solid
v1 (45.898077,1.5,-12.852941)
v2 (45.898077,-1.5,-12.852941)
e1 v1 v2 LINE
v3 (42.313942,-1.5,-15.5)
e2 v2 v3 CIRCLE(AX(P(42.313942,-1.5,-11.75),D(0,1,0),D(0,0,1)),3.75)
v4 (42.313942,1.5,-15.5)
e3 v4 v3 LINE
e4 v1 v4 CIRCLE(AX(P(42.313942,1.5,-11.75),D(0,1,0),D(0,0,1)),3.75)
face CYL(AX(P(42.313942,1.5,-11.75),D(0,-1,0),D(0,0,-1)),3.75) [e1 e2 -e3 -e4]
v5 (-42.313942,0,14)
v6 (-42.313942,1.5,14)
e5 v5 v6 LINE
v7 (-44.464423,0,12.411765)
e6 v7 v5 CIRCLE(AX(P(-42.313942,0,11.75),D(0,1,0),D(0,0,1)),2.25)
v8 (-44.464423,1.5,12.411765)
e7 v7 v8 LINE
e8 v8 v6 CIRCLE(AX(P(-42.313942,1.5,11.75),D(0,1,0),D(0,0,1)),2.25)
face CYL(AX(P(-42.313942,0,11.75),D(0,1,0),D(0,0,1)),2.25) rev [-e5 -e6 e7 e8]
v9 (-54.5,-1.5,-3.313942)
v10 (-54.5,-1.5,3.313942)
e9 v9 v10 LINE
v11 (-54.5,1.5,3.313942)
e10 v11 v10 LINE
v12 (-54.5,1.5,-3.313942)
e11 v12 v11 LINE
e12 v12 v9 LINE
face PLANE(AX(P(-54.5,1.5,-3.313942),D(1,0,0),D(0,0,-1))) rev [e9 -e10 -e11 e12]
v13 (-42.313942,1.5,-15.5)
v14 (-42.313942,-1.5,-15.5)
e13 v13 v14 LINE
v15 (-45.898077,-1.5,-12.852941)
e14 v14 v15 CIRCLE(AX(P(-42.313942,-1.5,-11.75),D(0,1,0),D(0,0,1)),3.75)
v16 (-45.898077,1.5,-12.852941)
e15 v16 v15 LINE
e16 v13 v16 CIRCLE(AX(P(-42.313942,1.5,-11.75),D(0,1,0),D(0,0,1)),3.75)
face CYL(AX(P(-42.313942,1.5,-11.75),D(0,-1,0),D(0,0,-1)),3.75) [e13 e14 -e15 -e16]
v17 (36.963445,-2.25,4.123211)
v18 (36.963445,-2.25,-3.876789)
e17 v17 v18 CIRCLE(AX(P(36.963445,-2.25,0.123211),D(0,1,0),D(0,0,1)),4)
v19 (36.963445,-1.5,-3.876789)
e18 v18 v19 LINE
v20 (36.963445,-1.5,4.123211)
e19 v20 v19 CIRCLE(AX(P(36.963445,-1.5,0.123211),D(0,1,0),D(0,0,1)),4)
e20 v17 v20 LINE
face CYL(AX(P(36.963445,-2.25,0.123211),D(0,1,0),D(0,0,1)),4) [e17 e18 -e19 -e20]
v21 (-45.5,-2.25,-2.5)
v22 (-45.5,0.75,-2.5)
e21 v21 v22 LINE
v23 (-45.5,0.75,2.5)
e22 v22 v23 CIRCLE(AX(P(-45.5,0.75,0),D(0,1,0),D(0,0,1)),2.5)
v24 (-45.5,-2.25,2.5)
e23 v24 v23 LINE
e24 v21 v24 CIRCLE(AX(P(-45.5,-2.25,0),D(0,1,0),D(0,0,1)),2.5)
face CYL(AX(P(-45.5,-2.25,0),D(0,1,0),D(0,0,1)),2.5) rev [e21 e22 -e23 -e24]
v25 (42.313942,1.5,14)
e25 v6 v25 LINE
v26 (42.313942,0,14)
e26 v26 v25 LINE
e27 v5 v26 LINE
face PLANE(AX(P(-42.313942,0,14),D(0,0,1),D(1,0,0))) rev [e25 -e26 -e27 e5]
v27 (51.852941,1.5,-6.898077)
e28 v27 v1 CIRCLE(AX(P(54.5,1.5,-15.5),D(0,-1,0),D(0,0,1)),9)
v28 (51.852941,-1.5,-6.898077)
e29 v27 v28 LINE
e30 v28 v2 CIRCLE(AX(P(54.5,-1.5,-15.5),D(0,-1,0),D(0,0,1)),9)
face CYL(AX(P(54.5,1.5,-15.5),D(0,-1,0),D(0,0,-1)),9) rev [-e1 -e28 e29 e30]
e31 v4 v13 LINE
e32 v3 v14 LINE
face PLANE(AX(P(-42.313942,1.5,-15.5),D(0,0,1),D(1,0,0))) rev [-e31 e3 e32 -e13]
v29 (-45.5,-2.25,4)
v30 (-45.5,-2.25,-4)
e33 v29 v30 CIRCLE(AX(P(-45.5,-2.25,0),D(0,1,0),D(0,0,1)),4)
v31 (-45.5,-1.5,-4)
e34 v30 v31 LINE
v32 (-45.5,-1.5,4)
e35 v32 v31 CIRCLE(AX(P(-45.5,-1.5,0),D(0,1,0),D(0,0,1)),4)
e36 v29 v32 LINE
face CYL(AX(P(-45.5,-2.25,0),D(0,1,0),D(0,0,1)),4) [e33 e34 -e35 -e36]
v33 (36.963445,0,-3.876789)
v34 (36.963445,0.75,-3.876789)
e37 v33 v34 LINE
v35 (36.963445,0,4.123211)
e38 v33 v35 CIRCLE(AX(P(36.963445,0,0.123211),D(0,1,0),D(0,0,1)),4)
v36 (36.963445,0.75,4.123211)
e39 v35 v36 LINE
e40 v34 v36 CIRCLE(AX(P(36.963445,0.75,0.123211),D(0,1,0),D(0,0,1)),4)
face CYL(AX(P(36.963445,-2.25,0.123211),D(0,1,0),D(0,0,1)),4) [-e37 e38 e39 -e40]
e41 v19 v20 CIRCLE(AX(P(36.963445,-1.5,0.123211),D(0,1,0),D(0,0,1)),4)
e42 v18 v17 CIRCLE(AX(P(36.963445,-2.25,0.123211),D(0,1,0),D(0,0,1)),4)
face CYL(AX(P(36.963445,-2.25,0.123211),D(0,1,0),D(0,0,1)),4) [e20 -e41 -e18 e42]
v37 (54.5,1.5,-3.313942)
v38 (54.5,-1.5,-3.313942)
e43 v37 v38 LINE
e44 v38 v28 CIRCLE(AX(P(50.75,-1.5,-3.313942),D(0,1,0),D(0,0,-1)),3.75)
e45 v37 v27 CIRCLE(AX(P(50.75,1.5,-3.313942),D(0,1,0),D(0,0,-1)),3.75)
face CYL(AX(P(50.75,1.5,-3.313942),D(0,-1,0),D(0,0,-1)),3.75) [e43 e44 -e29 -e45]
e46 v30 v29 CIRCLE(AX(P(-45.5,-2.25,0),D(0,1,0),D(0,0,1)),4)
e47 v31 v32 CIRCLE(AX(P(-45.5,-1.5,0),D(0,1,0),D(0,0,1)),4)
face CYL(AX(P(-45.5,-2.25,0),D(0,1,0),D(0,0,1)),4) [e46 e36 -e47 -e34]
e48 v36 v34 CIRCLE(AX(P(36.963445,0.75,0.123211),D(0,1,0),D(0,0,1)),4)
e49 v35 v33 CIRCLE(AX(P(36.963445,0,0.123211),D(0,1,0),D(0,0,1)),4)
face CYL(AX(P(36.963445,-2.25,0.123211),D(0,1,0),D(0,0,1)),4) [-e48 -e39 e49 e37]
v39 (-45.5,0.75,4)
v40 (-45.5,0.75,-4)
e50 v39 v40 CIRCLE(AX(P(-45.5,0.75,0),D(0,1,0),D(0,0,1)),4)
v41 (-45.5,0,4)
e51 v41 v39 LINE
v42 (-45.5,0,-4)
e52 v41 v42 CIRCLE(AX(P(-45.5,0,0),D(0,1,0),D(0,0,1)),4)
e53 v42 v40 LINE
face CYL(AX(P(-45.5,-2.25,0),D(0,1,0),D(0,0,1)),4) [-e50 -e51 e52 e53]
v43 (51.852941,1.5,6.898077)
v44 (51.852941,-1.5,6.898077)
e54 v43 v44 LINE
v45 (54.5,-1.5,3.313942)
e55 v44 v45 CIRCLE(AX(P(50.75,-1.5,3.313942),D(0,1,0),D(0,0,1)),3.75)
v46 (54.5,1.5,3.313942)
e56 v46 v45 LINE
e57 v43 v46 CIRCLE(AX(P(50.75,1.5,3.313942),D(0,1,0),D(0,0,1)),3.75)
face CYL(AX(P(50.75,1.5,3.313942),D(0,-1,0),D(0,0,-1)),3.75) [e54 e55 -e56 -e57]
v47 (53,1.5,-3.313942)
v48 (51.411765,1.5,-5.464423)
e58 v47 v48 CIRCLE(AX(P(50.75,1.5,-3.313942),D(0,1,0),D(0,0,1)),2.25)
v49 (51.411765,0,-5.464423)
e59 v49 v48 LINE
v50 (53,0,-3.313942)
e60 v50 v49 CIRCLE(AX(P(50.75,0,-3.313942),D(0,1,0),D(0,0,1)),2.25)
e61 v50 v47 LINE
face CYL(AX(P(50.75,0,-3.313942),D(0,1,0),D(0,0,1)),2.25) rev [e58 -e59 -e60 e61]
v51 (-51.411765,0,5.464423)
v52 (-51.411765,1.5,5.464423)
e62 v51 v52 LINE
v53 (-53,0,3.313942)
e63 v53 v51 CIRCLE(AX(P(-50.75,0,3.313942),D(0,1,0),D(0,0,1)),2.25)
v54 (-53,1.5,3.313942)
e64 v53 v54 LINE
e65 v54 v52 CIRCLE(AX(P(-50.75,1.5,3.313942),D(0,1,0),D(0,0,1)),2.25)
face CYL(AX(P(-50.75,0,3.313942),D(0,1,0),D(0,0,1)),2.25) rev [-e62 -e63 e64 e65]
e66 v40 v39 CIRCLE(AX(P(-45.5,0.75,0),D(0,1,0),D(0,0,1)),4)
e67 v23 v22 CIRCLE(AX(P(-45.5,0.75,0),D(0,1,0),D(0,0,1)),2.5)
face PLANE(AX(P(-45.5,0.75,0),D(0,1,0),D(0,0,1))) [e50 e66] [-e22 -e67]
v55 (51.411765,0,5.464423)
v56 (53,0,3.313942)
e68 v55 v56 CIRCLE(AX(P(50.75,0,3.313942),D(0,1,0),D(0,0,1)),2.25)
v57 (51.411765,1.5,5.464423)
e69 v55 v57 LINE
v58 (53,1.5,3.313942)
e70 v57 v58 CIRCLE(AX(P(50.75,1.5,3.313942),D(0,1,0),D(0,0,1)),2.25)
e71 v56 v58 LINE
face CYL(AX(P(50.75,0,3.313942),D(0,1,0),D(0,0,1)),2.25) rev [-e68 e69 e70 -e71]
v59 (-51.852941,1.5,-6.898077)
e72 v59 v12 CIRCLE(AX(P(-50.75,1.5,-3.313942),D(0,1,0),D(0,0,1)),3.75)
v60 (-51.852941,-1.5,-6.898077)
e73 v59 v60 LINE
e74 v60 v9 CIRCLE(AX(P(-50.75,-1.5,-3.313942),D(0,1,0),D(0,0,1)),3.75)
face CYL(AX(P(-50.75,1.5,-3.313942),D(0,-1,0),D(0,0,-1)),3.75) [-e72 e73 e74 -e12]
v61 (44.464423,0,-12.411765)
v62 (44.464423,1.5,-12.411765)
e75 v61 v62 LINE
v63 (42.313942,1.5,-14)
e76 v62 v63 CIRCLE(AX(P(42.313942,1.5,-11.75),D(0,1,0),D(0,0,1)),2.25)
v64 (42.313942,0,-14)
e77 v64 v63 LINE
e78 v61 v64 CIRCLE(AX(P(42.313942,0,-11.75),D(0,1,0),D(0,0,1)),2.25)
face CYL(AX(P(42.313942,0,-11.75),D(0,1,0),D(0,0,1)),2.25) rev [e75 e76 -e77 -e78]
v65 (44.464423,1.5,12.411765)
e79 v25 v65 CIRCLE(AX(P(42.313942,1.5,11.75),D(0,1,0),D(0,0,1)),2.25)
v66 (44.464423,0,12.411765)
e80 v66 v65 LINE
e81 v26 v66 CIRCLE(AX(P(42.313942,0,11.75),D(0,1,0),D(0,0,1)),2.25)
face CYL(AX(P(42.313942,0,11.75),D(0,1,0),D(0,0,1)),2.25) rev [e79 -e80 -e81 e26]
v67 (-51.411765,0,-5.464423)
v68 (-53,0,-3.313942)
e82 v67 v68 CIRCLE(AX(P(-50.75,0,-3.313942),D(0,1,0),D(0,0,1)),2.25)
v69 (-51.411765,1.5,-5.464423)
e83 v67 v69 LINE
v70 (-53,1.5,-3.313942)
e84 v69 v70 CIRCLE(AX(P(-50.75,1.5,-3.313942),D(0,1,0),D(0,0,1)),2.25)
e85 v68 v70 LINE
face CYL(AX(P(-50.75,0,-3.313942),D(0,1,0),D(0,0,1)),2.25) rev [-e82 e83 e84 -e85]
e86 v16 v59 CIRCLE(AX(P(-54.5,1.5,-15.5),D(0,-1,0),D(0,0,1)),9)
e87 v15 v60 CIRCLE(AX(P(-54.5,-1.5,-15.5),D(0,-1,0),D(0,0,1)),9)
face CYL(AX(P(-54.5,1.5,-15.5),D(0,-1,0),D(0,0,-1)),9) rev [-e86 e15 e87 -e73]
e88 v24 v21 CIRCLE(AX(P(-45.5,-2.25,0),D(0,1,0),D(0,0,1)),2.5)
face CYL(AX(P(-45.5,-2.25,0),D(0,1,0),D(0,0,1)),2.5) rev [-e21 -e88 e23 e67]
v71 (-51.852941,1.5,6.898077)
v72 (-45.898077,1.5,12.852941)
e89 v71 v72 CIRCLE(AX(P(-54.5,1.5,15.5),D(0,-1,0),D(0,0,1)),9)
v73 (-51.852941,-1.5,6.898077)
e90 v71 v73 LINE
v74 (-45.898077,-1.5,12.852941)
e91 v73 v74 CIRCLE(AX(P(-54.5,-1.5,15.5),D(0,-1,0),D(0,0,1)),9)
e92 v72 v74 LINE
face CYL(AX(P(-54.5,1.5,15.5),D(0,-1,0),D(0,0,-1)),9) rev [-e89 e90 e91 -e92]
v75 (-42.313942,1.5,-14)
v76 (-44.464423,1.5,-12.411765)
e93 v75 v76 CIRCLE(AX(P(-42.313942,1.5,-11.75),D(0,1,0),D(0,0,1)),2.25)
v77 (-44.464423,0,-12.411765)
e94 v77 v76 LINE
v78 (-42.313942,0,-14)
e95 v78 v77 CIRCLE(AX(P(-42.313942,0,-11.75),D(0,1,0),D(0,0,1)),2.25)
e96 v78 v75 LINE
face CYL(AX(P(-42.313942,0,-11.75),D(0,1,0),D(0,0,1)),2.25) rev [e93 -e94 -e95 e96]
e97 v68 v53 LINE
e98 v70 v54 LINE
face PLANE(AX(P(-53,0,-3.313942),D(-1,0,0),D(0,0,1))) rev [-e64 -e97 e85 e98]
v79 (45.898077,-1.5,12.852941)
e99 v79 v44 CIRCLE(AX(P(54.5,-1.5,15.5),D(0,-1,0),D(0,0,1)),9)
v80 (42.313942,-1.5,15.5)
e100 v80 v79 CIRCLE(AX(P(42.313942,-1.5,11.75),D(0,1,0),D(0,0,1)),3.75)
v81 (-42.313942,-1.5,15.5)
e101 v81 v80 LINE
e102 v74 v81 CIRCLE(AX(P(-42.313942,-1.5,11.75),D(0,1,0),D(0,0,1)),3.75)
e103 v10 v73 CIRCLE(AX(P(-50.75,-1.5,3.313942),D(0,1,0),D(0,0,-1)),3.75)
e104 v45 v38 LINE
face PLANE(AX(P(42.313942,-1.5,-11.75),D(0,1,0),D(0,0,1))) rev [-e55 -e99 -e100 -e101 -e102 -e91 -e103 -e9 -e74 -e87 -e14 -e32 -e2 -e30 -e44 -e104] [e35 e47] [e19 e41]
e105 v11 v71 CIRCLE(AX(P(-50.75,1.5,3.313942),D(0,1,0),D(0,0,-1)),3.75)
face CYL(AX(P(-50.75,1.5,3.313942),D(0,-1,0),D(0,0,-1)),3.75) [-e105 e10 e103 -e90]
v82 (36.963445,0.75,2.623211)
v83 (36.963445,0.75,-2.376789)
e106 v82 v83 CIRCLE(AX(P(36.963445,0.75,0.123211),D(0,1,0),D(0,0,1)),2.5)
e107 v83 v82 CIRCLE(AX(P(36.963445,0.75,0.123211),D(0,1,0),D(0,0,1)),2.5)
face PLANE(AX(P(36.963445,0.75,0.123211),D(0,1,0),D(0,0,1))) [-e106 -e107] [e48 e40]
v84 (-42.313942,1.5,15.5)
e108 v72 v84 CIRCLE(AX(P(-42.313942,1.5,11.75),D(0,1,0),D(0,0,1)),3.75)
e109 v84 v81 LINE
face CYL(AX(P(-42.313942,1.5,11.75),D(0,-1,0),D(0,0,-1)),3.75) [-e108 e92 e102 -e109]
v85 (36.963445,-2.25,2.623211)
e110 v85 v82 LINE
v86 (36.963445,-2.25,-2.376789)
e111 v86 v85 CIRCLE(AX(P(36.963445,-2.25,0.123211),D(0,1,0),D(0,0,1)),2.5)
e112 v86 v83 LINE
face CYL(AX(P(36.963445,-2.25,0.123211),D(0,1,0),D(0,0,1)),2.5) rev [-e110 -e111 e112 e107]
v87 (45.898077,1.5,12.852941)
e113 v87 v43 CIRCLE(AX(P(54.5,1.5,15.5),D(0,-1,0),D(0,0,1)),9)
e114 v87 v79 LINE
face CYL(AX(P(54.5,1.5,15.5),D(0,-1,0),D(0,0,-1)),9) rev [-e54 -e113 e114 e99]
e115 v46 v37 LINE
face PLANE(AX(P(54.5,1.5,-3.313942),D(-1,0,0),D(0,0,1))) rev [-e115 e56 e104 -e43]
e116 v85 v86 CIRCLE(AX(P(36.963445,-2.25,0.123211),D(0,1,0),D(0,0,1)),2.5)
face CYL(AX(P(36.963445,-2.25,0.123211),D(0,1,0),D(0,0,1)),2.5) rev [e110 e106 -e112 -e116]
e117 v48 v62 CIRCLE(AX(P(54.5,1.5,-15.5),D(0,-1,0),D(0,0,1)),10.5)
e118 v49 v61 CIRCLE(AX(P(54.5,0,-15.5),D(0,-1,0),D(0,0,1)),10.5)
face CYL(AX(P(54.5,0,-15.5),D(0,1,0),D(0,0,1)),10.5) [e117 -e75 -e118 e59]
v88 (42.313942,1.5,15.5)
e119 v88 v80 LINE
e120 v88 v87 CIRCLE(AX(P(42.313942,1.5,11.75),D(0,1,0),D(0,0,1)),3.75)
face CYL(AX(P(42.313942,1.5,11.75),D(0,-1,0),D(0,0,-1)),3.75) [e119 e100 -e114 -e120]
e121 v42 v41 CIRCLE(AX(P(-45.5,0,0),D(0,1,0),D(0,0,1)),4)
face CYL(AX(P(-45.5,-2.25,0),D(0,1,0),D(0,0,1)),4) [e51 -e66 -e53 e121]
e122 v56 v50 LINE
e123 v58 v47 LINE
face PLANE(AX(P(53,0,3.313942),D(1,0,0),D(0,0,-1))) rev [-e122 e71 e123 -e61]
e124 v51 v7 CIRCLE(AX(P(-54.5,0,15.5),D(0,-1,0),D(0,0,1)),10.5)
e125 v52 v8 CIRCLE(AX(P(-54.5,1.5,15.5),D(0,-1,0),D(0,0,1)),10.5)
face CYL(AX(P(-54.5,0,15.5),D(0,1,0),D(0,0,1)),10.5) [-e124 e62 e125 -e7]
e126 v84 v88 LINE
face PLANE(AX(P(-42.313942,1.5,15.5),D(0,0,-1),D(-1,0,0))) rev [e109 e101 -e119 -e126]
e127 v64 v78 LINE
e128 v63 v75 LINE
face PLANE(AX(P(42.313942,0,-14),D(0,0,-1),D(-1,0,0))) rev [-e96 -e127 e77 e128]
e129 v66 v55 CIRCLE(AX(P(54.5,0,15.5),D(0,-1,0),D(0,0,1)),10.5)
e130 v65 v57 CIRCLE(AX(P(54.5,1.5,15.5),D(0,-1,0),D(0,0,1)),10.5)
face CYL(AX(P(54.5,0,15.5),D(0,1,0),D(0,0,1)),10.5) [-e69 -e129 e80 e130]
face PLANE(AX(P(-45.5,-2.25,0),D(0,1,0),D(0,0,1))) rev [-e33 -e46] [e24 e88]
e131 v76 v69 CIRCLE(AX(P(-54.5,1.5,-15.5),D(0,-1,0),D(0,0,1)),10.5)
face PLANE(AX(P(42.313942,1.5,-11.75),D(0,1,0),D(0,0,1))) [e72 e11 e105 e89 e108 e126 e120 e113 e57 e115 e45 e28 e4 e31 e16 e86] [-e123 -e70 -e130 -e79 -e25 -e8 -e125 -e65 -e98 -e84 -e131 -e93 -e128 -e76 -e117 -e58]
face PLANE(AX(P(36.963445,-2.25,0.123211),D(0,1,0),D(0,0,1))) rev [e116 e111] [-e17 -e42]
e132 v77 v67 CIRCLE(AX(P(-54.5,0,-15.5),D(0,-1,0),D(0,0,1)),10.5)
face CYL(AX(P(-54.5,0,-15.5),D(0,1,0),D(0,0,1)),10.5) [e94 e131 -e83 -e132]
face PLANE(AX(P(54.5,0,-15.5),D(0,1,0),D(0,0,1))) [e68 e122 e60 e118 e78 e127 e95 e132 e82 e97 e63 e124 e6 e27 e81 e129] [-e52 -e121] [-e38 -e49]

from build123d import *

# Parameters (mm, degrees)
BASE_PLATE_DEPTH                = 1.5
TOP_RECESS_1_5MM_DEPTH          = 1.5
MOUNTING_HOLE_BOSSES_DEPTH      = 0.75
MOUNTING_HOLE_BOSSES_DEPTH_BACK = 2.25
HOLE_BOSS_SKETCH_R              = 4
HOLE_BOSS_SKETCH_R_2            = 2.5
MOUNTING_HOLE_SKETCH_R          = 2.5
MOUNTING_HOLES_2X_DEPTH         = 30.75


with BuildPart() as part:
    # Plate Outline Sketch → Base Plate (new, symmetric)
    with BuildSketch(Plane(origin=(0, 0, 0), x_dir=(1, 0, 0), z_dir=(0, 1, 0))):
        with BuildLine():
            Line((-42.313942393, 15.5), (42.313942393, 15.5))
            ThreePointArc((42.313942393, 15.5), (44.541774365, 14.76649875), (45.898076983, 12.852941176))
            ThreePointArc((45.898076983, 12.852941176), (48.136038969, 9.136038969), (51.852941176, 6.898076983))
            ThreePointArc((51.852941176, 6.898076983), (53.76649875, 5.541774365), (54.5, 3.313942393))
            Line((54.5, 3.313942393), (54.5, -3.313942393))
            ThreePointArc((54.5, -3.313942393), (53.76649875, -5.541774365), (51.852941176, -6.898076983))
            ThreePointArc((51.852941176, -6.898076983), (48.136038969, -9.136038969), (45.898076983, -12.852941176))
            ThreePointArc((45.898076983, -12.852941176), (44.541774365, -14.76649875), (42.313942393, -15.5))
            Line((42.313942393, -15.5), (-42.313942393, -15.5))
            ThreePointArc((-42.313942393, -15.5), (-44.541774365, -14.76649875), (-45.898076983, -12.852941176))
            ThreePointArc((-45.898076983, -12.852941176), (-48.136038969, -9.136038969), (-51.852941176, -6.898076983))
            ThreePointArc((-51.852941176, -6.898076983), (-53.76649875, -5.541774365), (-54.5, -3.313942393))
            Line((-54.5, -3.313942393), (-54.5, 3.313942393))
            ThreePointArc((-54.5, 3.313942393), (-53.76649875, 5.541774365), (-51.852941176, 6.898076983))
            ThreePointArc((-51.852941176, 6.898076983), (-48.136038969, 9.136038969), (-45.898076983, 12.852941176))
            ThreePointArc((-45.898076983, 12.852941176), (-44.541774365, 14.76649875), (-42.313942393, 15.5))
        make_face()
    extrude(amount=BASE_PLATE_DEPTH, both=True)

    # Recess Outline Sketch → Top Recess 1.5mm (cut)
    with BuildSketch(Plane(origin=(0, 1.5, 0), x_dir=(1, 0, 0), z_dir=(0, 1, 0))):
        with BuildLine():
            Line((42.313942393, 14), (-42.313942393, 14))
            ThreePointArc((-42.313942393, 14), (-43.650641576, 13.55989925), (-44.464423147, 12.411764706))
            ThreePointArc((-44.464423147, 12.411764706), (-47.075378798, 8.075378798), (-51.411764706, 5.464423147))
            ThreePointArc((-51.411764706, 5.464423147), (-52.55989925, 4.650641576), (-53, 3.313942393))
            Line((-53, 3.313942393), (-53, -3.313942393))
            ThreePointArc((-53, -3.313942393), (-52.55989925, -4.650641576), (-51.411764706, -5.464423147))
            ThreePointArc((-51.411764706, -5.464423147), (-47.075378798, -8.075378798), (-44.464423147, -12.411764706))
            ThreePointArc((-44.464423147, -12.411764706), (-43.650641576, -13.55989925), (-42.313942393, -14))
            Line((-42.313942393, -14), (42.313942393, -14))
            ThreePointArc((42.313942393, -14), (43.650641576, -13.55989925), (44.464423147, -12.411764706))
            ThreePointArc((44.464423147, -12.411764706), (47.075378798, -8.075378798), (51.411764706, -5.464423147))
            ThreePointArc((51.411764706, -5.464423147), (52.55989925, -4.650641576), (53, -3.313942393))
            Line((53, -3.313942393), (53, 3.313942393))
            ThreePointArc((53, 3.313942393), (52.55989925, 4.650641576), (51.411764706, 5.464423147))
            ThreePointArc((51.411764706, 5.464423147), (47.075378798, 8.075378798), (44.464423147, 12.411764706))
            ThreePointArc((44.464423147, 12.411764706), (43.650641576, 13.55989925), (42.313942393, 14))
        make_face()
    extrude(amount=-TOP_RECESS_1_5MM_DEPTH, mode=Mode.SUBTRACT)

    # Hole Boss Sketch → Mounting Hole Bosses (add, two sides: drawn at the far end of the back side and taken through both)
    # profile 1 of 2: a face of its own
    with BuildSketch(Plane(origin=(0, 0, 0), x_dir=(1, 0, 0), z_dir=(0, 1, 0)).offset(-MOUNTING_HOLE_BOSSES_DEPTH_BACK)):
        with Locations(Location((-45.5, 0, 0), (0, 0, 270))):
            Circle(HOLE_BOSS_SKETCH_R)
        with Locations(Location((-45.5, 0, 0), (0, 0, 270))):
            Circle(HOLE_BOSS_SKETCH_R_2, mode=Mode.SUBTRACT)
    # profile 2 of 2: a face of its own
    with BuildSketch(Plane(origin=(0, 0, 0), x_dir=(1, 0, 0), z_dir=(0, 1, 0)).offset(-MOUNTING_HOLE_BOSSES_DEPTH_BACK)):
        with Locations(Location((36.963444552, -0.123211482, 0), (0, 0, 270))):
            Circle(HOLE_BOSS_SKETCH_R)
        with Locations(Location((36.963444552, -0.123211482, 0), (0, 0, 270))):
            Circle(HOLE_BOSS_SKETCH_R_2, mode=Mode.SUBTRACT)
    extrude(amount=MOUNTING_HOLE_BOSSES_DEPTH + MOUNTING_HOLE_BOSSES_DEPTH_BACK)

    # Mounting Hole Sketch → Mounting Holes 2x (cut)
    with BuildSketch(Plane(origin=(0, 0, 0), x_dir=(1, 0, 0), z_dir=(0, 1, 0))):
        with Locations(Location((36.963444552, -0.123211482, 0), (0, 0, 270))):
            Circle(MOUNTING_HOLE_SKETCH_R)
        with Locations(Location((-45.5, 0, 0), (0, 0, 270))):
            Circle(MOUNTING_HOLE_SKETCH_R)
    extrude(amount=-MOUNTING_HOLES_2X_DEPTH, mode=Mode.SUBTRACT)


solid = part.part
